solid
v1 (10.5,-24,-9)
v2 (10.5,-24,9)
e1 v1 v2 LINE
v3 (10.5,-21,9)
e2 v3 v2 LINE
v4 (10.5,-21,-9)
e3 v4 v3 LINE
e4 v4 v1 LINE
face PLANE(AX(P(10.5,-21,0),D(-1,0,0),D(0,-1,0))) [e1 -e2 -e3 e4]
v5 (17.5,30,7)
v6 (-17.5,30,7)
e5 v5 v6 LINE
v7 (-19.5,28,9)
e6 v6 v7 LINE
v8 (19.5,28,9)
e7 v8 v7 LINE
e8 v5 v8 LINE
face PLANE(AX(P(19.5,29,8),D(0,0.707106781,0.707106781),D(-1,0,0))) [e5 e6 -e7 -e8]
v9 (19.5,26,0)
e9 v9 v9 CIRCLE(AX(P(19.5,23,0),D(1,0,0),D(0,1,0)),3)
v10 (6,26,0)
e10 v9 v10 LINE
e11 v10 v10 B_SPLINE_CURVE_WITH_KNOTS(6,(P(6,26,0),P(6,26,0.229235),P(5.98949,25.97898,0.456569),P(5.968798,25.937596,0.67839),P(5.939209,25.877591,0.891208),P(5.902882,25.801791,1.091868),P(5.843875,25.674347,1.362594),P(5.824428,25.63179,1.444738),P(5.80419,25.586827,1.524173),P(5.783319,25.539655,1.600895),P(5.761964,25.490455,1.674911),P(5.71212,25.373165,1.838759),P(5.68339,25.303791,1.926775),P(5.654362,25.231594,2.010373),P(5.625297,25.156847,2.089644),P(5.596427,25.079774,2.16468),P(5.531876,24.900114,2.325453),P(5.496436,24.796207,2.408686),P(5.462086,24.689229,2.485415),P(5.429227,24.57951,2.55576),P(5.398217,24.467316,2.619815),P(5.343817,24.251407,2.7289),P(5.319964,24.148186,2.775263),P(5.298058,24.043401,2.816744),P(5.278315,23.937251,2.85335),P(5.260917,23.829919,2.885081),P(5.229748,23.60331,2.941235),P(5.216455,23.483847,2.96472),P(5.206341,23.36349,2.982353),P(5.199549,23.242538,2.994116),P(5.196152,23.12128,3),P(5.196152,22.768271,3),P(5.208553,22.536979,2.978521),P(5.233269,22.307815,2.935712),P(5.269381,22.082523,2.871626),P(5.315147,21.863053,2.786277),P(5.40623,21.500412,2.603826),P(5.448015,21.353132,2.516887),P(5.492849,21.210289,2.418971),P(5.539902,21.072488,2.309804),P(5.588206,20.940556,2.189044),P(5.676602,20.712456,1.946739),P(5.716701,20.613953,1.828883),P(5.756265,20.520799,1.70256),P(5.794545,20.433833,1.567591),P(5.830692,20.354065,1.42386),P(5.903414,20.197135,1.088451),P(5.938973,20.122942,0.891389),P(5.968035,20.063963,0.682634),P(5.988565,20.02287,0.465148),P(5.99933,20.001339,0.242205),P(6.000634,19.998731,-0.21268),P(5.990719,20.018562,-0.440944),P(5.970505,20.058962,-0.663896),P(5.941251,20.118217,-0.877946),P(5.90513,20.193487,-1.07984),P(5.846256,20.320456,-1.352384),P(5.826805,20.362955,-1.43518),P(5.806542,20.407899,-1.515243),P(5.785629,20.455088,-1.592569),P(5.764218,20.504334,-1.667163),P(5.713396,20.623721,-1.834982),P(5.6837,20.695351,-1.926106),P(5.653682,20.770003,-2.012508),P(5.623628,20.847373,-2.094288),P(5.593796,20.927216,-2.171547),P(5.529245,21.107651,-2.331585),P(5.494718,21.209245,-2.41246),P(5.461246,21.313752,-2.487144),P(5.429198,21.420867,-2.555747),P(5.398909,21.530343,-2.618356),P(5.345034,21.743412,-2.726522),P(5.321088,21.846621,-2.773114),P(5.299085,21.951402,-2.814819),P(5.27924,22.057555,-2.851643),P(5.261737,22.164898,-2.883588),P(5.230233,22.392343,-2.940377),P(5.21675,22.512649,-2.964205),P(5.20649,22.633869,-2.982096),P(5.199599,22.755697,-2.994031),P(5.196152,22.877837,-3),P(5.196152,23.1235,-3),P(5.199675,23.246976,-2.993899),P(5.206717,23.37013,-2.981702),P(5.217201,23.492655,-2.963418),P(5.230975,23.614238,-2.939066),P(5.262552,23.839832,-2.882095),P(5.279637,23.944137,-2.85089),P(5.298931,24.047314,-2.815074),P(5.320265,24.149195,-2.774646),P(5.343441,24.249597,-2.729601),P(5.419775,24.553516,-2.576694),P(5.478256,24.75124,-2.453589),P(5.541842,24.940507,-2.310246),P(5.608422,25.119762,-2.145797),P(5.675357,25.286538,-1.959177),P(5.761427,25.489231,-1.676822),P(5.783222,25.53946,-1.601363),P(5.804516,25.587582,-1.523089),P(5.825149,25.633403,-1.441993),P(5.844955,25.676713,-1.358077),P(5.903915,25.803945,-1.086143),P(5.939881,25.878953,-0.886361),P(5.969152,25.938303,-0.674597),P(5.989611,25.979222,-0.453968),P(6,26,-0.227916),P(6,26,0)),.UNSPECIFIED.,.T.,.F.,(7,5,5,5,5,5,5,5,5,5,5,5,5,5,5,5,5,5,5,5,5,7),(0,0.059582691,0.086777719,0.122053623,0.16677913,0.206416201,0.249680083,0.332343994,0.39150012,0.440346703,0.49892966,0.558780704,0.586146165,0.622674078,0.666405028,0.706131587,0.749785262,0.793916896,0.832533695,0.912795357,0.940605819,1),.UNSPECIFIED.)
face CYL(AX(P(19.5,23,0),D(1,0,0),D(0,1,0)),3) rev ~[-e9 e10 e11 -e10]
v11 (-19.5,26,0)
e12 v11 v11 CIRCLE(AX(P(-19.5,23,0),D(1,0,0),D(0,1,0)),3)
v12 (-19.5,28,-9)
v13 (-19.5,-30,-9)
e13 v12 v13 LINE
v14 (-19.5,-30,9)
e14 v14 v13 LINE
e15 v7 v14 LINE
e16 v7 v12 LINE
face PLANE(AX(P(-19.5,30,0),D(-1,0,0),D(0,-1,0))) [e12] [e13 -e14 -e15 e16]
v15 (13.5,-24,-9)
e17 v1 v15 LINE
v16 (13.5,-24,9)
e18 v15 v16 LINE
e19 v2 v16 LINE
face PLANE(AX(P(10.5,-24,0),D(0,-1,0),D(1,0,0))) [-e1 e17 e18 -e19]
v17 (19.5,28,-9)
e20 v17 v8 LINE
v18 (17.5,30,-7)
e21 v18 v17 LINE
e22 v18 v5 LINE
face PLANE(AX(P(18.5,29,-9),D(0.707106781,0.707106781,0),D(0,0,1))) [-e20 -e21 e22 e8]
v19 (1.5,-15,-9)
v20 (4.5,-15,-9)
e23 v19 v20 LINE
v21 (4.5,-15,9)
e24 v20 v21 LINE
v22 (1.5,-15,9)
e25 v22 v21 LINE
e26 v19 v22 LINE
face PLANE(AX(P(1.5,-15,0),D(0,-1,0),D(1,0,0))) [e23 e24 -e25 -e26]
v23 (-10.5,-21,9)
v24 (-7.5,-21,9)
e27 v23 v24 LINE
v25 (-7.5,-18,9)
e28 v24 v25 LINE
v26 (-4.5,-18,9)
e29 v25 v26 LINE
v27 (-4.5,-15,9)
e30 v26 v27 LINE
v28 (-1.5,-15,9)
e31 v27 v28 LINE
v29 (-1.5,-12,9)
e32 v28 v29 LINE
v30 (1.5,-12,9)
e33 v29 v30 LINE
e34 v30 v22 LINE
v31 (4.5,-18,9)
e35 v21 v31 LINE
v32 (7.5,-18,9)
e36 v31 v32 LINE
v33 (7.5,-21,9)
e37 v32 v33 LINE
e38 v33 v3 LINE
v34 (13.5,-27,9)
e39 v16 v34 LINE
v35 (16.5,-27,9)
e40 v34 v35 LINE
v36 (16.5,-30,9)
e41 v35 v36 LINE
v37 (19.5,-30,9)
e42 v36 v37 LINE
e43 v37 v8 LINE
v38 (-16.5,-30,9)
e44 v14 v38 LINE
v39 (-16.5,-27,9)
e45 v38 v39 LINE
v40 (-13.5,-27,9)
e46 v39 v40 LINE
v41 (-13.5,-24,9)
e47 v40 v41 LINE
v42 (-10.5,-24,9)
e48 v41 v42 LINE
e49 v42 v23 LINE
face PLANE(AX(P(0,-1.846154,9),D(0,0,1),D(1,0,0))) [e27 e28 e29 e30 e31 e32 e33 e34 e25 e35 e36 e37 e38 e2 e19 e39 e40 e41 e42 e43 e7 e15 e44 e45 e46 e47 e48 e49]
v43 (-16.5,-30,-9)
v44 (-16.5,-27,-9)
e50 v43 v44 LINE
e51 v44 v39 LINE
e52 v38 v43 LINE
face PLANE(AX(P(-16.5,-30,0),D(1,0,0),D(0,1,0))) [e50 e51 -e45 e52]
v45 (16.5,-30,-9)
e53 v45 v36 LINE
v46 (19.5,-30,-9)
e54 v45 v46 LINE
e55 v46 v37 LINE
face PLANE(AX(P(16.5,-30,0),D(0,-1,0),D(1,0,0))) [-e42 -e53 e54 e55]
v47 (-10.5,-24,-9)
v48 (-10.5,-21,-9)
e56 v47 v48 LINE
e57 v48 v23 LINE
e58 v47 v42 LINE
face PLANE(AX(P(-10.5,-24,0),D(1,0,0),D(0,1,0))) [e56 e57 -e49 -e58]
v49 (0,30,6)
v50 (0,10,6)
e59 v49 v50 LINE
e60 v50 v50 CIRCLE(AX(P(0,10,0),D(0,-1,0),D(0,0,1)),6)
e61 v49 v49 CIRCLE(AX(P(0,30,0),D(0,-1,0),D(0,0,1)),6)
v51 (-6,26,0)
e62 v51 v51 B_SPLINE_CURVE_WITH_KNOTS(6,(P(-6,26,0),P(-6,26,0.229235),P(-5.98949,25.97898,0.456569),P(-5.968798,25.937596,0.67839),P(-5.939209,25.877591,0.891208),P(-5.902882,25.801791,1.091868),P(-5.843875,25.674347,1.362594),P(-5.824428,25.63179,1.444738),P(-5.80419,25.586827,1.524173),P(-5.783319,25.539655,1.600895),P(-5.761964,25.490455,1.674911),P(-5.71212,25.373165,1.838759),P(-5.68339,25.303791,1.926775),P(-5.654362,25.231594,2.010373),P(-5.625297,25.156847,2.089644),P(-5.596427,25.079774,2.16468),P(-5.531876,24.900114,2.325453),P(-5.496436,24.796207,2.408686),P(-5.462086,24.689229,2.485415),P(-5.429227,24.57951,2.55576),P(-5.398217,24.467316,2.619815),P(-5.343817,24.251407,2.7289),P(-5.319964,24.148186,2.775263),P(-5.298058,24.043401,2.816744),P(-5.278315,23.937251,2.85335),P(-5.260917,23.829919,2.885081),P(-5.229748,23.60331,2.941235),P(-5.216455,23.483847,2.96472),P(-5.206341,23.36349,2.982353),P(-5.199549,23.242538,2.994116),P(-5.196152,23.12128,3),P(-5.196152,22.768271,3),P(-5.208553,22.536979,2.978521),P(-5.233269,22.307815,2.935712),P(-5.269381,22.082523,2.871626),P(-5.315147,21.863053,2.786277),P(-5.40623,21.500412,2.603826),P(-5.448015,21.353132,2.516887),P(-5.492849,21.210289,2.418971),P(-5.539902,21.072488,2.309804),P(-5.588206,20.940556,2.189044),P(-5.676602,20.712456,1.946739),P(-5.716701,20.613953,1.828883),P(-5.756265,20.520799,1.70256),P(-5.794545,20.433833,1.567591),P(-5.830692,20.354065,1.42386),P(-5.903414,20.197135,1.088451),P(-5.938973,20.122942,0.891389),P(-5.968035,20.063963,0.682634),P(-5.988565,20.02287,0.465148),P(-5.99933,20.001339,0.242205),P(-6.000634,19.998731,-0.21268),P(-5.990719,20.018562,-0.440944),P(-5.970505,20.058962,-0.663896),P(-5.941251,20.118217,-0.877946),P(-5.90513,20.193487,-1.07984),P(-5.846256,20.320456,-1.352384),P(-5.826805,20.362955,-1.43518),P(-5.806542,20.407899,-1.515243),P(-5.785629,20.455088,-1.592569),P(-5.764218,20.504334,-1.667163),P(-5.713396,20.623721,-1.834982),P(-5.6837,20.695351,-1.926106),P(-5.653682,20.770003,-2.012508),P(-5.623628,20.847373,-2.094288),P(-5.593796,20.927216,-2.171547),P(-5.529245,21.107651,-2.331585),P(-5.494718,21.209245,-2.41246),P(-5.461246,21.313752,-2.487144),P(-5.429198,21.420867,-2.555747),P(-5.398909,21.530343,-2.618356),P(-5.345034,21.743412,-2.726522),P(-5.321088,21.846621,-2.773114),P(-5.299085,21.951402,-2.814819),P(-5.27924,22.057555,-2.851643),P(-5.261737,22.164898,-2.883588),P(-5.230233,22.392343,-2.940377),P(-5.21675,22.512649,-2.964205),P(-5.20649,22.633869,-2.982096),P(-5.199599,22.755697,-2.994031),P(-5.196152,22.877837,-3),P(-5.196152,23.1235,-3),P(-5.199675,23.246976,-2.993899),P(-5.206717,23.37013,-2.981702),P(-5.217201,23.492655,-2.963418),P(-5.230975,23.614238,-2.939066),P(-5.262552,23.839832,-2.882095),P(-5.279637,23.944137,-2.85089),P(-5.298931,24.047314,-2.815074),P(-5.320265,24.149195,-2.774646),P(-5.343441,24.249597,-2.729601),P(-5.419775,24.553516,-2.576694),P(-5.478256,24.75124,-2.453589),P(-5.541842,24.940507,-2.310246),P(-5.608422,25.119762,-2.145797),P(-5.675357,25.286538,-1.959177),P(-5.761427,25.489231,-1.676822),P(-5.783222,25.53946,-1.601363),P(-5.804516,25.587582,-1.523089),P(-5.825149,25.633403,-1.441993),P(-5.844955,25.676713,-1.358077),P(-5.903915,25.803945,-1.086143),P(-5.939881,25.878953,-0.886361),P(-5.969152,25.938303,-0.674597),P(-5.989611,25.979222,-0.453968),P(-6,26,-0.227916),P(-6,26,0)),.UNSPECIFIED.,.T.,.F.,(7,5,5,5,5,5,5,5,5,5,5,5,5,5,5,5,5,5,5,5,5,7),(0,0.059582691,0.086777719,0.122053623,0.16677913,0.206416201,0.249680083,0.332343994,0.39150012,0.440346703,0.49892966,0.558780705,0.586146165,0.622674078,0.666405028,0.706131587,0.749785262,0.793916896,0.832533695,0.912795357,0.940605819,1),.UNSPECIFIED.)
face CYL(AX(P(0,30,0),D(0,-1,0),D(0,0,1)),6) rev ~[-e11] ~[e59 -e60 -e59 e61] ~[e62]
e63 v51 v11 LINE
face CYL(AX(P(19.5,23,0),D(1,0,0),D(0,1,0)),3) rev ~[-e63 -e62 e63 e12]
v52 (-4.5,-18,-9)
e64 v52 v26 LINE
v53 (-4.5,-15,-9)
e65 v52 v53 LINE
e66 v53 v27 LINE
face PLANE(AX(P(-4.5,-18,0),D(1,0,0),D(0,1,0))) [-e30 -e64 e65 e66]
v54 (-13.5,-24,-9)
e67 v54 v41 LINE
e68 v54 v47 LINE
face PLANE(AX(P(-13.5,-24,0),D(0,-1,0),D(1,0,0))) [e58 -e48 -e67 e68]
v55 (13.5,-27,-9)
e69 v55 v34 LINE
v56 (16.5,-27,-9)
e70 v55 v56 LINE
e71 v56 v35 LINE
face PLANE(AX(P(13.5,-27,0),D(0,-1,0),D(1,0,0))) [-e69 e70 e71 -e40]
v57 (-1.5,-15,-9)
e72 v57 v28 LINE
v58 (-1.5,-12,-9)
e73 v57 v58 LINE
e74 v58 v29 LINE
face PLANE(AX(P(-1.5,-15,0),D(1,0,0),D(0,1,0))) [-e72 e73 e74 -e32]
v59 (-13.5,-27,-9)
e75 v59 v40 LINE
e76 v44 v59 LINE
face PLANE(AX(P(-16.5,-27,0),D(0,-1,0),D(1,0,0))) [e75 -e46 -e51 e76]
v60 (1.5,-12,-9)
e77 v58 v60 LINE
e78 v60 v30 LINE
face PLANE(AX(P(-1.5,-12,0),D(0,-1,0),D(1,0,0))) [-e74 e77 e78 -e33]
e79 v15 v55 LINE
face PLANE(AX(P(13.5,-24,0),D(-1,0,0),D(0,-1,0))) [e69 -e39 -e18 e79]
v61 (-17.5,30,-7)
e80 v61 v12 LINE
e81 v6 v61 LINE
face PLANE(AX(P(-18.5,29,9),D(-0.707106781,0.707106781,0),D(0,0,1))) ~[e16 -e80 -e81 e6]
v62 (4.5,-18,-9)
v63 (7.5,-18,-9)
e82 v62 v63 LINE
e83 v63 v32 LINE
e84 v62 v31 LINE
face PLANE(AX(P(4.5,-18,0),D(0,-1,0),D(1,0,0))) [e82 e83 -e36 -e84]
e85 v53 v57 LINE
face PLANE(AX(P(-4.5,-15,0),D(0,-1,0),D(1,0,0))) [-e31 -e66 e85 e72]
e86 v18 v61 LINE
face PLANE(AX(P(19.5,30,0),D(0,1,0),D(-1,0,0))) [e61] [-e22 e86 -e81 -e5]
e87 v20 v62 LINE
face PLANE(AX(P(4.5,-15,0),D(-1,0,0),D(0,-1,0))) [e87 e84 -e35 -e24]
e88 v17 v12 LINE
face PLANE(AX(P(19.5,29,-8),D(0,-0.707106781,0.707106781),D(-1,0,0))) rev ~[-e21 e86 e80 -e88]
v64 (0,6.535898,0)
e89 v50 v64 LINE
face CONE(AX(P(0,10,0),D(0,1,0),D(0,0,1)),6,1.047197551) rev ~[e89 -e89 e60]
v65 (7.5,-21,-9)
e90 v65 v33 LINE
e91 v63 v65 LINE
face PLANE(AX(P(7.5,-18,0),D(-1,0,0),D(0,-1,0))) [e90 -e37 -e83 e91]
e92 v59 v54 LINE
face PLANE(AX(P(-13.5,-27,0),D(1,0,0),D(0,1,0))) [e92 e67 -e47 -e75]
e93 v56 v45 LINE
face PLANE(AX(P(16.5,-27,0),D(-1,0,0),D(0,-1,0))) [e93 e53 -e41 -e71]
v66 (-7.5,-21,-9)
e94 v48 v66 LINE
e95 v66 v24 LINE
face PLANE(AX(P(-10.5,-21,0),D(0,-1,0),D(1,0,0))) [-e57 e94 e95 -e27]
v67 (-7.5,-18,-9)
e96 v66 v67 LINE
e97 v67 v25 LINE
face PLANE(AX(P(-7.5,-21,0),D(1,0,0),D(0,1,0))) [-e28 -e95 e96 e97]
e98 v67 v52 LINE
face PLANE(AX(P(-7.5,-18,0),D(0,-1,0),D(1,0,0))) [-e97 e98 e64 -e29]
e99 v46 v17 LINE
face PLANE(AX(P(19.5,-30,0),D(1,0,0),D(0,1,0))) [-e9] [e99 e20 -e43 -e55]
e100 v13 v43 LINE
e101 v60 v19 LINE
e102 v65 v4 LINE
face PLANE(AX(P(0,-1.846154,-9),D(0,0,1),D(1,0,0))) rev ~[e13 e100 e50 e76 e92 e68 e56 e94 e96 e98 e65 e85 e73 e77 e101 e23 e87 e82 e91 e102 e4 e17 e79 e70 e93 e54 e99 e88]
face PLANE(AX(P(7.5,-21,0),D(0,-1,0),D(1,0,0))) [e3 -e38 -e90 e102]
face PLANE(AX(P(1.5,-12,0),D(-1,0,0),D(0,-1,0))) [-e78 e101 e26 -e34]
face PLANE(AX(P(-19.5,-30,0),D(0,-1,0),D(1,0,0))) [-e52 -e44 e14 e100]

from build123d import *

# Parameters (mm, degrees)
BOSS_EXTRUDE1_DEPTH = 9
CHAMFER1_SIZE       = 2
SKETCH2_R           = 3
CUT_EXTRUDE1_DEPTH  = 51.019996002


with BuildPart() as part:
    # Sketch1 → Boss-Extrude1 (new, symmetric)
    with BuildSketch(Plane.XY):
        Polygon((-16.5, -30), (-16.5, -27), (-13.5, -27), (-13.5, -24), (-10.5, -24), (-10.5, -21), (-7.5, -21), (-7.5, -18), (-4.5, -18), (-4.5, -15), (-1.5, -15), (-1.5, -12), (1.5, -12), (1.5, -15), (4.5, -15), (4.5, -18), (7.5, -18), (7.5, -21), (10.5, -21), (10.5, -24), (13.5, -24), (13.5, -27), (16.5, -27), (16.5, -30), (19.5, -30), (19.5, 30), (-19.5, 30), (-19.5, -30), align=None)
    extrude(amount=BOSS_EXTRUDE1_DEPTH, both=True)

    # Chamfer1
    chamfer1_edges = [part.edges().sort_by_distance(p)[0] for p in [
        (0, 30, 9),
        (0, 30, -9),
        (-19.5, 30, 0),
        (19.5, 30, 0),
    ]]
    chamfer(chamfer1_edges, length=CHAMFER1_SIZE)

    # Sketch2 → Cut-Extrude1 (cut, through all)
    with BuildSketch(Plane(origin=(19.5, 0, 0), x_dir=(0, 0, -1), z_dir=(1, 0, 0))):
        with Locations(Location((0, 23, 0), (0, 0, 90))):
            Circle(SKETCH2_R)
    extrude(amount=-CUT_EXTRUDE1_DEPTH, mode=Mode.SUBTRACT)

    # Sketch3 → Cut-Revolve1 (revolve, cut)
    with BuildSketch(Plane.XY, mode=Mode.PRIVATE) as cut_revolve1_sk:
        Polygon((0, 30), (6, 30), (6, 10), (0, 6.535898385), align=None)
    revolve(cut_revolve1_sk.sketch.rotate(Axis((0, 31.728134739, 0), (0, -1, 0)), 90), axis=Axis((0, 31.728134739, 0), (0, -1, 0)), mode=Mode.SUBTRACT)


solid = part.part
